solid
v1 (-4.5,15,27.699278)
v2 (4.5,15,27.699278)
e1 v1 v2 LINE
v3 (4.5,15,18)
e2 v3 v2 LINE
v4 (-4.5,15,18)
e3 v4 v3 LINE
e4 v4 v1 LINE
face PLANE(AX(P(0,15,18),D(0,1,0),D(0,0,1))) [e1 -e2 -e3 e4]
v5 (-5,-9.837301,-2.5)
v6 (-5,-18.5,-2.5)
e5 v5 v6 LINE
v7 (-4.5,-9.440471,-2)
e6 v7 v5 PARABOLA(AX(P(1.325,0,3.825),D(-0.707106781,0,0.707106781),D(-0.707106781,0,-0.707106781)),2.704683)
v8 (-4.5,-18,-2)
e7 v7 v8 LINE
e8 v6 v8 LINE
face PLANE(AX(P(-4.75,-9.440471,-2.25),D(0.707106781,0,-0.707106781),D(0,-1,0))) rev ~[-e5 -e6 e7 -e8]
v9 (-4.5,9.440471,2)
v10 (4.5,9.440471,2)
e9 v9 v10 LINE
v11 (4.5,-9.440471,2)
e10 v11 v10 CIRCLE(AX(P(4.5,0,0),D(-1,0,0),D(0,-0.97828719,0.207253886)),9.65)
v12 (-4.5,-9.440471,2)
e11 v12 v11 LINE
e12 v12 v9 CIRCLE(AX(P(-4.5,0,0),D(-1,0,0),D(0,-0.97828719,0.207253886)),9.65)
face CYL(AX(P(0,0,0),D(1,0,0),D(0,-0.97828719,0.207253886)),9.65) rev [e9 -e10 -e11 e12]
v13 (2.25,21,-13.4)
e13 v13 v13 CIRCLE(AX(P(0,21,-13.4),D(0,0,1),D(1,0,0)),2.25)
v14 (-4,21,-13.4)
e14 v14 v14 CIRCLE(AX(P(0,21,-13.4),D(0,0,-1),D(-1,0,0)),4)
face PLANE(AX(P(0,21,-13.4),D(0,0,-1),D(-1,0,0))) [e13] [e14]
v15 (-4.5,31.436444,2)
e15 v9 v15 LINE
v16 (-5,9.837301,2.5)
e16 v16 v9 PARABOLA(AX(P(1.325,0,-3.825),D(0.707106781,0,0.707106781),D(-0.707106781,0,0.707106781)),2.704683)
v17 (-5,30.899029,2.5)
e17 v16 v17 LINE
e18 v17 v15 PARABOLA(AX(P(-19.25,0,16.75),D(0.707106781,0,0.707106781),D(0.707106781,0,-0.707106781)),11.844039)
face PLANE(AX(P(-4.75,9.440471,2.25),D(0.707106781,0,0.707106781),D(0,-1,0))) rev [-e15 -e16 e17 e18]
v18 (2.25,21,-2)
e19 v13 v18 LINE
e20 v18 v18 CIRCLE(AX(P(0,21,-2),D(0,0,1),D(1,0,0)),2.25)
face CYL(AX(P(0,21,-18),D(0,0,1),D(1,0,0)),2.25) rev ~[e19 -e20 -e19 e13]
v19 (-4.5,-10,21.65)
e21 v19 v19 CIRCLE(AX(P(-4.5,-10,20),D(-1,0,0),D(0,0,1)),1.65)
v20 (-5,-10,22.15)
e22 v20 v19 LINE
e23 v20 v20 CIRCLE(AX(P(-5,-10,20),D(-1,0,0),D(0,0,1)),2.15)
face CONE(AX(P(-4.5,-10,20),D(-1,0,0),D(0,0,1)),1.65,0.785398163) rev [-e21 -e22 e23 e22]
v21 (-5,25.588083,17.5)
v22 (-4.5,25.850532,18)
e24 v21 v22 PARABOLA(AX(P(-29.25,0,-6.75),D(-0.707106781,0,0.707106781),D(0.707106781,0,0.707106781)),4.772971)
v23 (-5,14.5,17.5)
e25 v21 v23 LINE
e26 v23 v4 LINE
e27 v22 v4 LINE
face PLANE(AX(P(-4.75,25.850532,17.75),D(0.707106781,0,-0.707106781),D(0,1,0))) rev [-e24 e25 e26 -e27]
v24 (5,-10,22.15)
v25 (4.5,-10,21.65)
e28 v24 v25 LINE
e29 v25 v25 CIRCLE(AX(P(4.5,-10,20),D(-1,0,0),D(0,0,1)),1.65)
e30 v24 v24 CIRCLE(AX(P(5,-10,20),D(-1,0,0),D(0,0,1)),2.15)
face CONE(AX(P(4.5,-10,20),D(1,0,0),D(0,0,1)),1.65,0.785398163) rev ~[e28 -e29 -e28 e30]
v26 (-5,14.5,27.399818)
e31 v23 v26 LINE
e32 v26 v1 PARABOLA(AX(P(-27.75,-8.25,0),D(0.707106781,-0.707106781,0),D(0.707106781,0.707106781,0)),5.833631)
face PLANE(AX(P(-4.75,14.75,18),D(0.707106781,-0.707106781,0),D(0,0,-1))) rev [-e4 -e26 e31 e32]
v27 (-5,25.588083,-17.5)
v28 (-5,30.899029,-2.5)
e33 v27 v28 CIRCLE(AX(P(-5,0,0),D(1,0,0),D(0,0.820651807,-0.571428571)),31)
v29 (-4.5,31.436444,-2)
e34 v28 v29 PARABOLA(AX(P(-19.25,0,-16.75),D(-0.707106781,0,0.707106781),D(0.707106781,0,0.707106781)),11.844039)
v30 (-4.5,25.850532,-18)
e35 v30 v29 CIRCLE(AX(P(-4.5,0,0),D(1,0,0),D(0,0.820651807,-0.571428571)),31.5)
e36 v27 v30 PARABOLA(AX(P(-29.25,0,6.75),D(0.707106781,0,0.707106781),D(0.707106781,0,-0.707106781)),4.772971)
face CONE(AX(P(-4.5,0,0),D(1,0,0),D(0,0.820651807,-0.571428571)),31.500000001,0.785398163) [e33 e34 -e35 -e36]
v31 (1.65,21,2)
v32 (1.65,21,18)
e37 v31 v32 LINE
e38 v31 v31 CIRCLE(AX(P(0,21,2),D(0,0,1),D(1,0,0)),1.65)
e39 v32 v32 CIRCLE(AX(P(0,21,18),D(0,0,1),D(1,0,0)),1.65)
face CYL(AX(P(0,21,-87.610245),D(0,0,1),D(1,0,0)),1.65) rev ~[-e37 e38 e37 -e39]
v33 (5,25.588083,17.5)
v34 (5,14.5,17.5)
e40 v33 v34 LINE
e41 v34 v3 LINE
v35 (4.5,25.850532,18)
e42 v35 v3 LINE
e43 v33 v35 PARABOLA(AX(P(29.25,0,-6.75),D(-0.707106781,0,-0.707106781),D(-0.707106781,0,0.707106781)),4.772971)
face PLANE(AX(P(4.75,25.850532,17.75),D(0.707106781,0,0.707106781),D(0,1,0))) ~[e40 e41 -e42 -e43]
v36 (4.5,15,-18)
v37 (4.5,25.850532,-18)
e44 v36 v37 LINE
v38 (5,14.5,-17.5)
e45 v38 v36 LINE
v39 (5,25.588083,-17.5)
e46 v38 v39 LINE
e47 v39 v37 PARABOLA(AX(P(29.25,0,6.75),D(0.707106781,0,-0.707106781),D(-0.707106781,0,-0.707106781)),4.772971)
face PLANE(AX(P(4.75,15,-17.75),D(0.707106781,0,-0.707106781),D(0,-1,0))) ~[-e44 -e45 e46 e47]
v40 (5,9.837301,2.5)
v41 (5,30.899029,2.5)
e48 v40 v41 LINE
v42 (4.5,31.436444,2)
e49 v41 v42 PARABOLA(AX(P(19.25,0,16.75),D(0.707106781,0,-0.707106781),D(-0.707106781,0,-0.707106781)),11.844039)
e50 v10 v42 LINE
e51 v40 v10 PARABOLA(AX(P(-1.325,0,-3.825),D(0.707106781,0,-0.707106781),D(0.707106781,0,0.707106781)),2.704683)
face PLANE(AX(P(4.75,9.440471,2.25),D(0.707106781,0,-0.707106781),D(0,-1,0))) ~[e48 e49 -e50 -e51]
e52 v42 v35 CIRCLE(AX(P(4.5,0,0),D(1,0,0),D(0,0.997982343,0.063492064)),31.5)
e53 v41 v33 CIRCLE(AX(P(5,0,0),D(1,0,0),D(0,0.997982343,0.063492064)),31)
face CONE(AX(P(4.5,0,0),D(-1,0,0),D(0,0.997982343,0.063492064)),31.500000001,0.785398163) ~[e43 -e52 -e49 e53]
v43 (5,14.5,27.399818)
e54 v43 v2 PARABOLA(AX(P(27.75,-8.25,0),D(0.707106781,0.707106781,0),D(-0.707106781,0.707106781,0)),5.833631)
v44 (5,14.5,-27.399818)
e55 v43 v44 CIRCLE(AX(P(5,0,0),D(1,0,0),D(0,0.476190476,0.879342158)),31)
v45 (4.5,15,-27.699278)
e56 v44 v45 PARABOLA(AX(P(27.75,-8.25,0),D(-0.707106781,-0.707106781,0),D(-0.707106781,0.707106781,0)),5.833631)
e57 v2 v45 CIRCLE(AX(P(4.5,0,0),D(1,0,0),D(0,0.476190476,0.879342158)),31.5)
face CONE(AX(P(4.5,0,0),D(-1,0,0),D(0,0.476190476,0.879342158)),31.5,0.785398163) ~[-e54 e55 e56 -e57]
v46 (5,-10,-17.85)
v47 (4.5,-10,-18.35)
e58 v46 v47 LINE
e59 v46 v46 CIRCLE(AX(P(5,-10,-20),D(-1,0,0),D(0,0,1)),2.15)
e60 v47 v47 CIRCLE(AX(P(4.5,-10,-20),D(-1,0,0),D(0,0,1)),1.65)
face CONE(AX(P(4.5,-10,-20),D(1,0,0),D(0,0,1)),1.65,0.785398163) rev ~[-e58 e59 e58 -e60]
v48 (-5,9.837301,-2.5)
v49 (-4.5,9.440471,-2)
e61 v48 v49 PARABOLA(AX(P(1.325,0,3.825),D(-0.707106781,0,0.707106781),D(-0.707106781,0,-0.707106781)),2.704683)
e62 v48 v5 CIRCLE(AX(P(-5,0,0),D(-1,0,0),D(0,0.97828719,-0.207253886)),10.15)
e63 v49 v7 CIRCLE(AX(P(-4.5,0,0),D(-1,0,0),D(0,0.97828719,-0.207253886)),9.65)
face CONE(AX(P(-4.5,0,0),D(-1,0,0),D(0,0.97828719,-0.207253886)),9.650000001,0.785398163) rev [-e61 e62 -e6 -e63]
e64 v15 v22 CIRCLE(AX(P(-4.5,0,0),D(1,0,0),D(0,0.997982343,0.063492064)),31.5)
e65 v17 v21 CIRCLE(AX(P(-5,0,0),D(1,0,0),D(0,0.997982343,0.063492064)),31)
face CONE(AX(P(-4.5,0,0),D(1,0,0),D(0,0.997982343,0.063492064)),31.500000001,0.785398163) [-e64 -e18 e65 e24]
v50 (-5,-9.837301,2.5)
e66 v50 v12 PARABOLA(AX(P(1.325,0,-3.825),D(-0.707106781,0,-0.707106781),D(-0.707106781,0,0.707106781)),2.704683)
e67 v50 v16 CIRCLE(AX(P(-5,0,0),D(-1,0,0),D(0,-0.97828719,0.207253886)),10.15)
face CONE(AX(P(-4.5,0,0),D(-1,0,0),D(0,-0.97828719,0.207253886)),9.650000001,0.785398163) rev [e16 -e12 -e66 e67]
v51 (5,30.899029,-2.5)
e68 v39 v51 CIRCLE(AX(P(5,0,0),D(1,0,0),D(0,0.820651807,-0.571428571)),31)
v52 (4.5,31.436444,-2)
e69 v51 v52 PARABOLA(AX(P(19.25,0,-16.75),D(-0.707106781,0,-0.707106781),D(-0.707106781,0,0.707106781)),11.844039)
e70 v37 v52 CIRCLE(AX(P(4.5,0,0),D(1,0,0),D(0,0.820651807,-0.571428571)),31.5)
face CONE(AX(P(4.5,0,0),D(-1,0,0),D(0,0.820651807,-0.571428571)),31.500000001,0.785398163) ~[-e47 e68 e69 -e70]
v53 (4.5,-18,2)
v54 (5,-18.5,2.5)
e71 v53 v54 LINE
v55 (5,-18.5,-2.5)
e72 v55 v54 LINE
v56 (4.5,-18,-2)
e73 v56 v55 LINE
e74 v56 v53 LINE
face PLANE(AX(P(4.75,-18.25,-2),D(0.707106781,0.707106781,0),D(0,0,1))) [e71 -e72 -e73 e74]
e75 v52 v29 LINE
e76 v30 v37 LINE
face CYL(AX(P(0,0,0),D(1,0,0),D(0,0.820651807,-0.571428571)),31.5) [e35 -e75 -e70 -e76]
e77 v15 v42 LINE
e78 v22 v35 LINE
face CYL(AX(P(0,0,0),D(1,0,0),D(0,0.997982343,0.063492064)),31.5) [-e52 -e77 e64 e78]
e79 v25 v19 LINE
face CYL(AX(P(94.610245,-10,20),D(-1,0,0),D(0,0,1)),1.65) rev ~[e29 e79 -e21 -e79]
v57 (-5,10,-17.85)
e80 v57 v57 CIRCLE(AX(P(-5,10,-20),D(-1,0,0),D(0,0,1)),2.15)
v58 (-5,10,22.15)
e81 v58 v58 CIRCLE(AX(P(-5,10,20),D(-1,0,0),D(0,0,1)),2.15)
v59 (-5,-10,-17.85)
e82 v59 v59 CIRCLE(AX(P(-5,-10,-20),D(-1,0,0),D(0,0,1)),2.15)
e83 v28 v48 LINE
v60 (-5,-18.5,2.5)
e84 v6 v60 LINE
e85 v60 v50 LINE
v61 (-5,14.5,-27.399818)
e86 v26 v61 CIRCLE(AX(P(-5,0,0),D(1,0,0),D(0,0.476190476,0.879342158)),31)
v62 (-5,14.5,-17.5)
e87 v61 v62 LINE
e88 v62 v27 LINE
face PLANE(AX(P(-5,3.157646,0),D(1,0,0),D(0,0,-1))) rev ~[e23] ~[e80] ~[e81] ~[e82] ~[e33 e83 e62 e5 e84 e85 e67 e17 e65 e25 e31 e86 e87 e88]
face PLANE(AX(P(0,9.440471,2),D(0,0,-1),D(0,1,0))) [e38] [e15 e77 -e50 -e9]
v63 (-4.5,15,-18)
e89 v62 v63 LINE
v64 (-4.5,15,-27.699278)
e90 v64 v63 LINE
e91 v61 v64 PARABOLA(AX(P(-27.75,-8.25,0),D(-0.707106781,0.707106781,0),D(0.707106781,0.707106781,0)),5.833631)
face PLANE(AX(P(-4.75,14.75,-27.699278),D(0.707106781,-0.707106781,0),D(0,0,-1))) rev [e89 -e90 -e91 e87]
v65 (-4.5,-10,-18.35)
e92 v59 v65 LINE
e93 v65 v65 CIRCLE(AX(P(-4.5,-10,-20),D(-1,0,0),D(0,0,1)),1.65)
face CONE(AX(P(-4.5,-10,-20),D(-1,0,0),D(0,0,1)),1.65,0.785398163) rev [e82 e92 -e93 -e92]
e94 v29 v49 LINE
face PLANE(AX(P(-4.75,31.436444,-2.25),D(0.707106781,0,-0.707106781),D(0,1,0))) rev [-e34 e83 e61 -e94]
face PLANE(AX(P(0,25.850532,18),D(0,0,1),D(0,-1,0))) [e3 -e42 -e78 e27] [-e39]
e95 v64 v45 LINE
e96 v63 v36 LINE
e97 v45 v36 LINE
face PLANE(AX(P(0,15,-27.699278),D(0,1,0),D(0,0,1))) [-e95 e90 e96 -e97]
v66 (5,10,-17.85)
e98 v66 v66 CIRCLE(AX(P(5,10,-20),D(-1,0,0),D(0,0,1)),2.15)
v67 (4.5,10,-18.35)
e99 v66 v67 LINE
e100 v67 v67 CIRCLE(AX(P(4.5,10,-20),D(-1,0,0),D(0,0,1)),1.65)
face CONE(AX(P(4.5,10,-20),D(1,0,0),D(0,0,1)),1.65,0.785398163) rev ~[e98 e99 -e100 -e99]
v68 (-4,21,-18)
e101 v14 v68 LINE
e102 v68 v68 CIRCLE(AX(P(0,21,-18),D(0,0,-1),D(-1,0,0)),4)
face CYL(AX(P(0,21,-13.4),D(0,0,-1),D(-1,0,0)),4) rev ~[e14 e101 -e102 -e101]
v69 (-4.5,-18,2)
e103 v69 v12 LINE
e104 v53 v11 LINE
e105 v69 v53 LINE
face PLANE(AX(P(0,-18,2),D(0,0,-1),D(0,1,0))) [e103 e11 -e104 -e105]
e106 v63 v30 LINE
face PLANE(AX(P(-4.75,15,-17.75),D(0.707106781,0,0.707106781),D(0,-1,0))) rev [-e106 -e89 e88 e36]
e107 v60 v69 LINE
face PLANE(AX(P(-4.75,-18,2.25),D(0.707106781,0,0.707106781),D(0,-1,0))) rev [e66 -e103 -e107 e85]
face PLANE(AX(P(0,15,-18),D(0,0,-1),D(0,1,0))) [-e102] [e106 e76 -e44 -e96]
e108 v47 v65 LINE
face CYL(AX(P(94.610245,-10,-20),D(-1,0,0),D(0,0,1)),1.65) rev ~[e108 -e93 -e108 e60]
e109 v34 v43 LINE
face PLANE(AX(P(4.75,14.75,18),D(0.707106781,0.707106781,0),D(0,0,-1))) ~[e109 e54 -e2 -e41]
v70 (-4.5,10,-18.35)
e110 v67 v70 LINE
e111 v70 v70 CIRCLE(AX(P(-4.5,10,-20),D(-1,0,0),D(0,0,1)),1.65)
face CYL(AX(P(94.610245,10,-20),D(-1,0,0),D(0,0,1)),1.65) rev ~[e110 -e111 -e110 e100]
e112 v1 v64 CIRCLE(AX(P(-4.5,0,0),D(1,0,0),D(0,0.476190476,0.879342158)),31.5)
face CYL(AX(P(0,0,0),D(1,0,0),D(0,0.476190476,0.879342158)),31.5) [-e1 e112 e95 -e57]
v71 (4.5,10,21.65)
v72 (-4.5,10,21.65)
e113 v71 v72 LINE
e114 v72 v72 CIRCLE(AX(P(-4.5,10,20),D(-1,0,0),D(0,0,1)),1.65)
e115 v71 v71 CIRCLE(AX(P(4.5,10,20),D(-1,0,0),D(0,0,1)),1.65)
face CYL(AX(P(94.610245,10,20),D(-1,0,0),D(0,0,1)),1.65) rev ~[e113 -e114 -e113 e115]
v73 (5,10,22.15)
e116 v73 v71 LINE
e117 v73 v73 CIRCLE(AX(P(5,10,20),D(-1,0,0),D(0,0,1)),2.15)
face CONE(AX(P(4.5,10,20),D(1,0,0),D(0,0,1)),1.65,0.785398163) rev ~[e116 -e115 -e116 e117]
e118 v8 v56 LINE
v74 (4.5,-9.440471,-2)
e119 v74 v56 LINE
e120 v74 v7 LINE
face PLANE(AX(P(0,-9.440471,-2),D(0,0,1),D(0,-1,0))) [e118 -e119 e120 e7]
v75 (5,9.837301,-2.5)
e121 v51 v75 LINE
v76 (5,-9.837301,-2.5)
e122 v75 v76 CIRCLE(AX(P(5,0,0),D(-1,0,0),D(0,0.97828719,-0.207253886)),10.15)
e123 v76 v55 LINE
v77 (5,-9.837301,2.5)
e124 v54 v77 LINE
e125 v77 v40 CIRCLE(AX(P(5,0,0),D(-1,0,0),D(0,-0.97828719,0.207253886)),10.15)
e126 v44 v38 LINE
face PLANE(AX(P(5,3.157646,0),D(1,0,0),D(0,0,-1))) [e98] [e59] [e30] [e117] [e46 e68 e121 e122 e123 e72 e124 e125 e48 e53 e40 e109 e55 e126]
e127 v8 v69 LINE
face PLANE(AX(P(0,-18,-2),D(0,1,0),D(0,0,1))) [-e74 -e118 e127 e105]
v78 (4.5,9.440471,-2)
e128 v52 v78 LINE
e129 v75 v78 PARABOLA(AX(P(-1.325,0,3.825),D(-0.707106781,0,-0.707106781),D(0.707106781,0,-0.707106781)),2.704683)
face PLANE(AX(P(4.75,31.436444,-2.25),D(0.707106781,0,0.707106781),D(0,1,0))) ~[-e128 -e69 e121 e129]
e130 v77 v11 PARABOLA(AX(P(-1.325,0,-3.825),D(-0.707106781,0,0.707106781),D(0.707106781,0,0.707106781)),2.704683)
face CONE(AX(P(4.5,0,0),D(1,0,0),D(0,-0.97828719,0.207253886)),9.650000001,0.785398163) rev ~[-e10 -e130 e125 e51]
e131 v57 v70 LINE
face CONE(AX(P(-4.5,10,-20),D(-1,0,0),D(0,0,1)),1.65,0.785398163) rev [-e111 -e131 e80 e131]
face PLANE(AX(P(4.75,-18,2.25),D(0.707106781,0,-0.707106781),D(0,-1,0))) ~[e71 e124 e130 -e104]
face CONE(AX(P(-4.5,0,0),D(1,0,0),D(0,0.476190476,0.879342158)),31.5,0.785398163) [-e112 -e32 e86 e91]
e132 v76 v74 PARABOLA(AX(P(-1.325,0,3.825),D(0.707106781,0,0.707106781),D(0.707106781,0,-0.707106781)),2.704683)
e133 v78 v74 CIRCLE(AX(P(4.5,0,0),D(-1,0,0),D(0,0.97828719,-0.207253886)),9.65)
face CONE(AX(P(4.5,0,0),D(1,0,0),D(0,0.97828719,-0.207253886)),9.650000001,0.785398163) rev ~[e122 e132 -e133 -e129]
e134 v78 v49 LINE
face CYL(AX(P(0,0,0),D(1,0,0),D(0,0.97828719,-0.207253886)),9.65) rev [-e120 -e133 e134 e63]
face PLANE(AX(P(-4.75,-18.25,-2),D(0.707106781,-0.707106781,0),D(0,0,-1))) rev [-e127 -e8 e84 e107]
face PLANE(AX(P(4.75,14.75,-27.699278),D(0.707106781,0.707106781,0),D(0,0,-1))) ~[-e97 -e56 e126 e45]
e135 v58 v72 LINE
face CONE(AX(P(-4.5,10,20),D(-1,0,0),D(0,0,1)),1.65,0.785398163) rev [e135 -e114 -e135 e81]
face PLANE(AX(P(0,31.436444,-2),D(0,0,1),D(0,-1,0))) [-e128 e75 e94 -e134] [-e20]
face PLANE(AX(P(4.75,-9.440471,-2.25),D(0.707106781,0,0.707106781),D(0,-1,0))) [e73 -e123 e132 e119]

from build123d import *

# Parameters (mm, degrees)
BOSS_EXTRUDE1_DEPTH                                  = 5
HOLE_SIZE_BY_SOCKET_HEAD_CAP_SCREW_TYPE1_D           = 4.5
HOLE_SIZE_BY_SOCKET_HEAD_CAP_SCREW_TYPE1_DEPTH       = 16
HOLE_SIZE_BY_SOCKET_HEAD_CAP_SCREW_TYPE1_CBORE_D     = 8
HOLE_SIZE_BY_SOCKET_HEAD_CAP_SCREW_TYPE1_CBORE_DEPTH = 4.6
M4_TAPPED_HOLE1_D                                    = 3.3
M4_TAPPED_HOLE2_D                                    = 3.3
CHAMFER1_SIZE                                        = 0.5


with BuildPart() as part:
    # Sketch1 → Boss-Extrude1 (new, symmetric)
    with BuildSketch(Plane(origin=(0, 0, 0), x_dir=(0, 0, -1), z_dir=(1, 0, 0))):
        with BuildLine():
            Line((2, -9.440471387), (2, -18))
            Line((2, -18), (-2, -18))
            Line((-2, -18), (-2, -9.440471387))
            ThreePointArc((-2, -9.440471387), (-9.65, 0), (-2, 9.440471387))
            Line((-2, 9.440471387), (-2, 31.436443819))
            ThreePointArc((-2, 31.436443819), (-10.382706919, 29.739693963), (-18, 25.850531909))
            Line((-18, 25.850531909), (-18, 15))
            Line((-18, 15), (-27.699277969, 15))
            ThreePointArc((-27.699277969, 15), (0, -31.5), (27.699277969, 15))
            Line((27.699277969, 15), (18, 15))
            Line((18, 15), (18, 25.850531909))
            ThreePointArc((18, 25.850531909), (10.382706919, 29.739693963), (2, 31.436443819))
            Line((2, 31.436443819), (2, 9.440471387))
            ThreePointArc((2, 9.440471387), (9.65, 0), (2, -9.440471387))
        make_face()
    extrude(amount=BOSS_EXTRUDE1_DEPTH, both=True)

    # Hole size by socket head cap screw type1
    with Locations(Plane(origin=(0, 0, -18), x_dir=(-1, 0, 0), z_dir=(0, 0, -1))):
        with Locations((0, 21)):
            CounterBoreHole(HOLE_SIZE_BY_SOCKET_HEAD_CAP_SCREW_TYPE1_D / 2, HOLE_SIZE_BY_SOCKET_HEAD_CAP_SCREW_TYPE1_CBORE_D / 2, HOLE_SIZE_BY_SOCKET_HEAD_CAP_SCREW_TYPE1_CBORE_DEPTH, depth=HOLE_SIZE_BY_SOCKET_HEAD_CAP_SCREW_TYPE1_DEPTH)

    # M4 Tapped Hole1 (through all)
    with Locations(Plane(origin=(0, 0, 2), x_dir=(-1, 0, 0), z_dir=(0, 0, -1))):
        with Locations((0, 21)):
            Hole(M4_TAPPED_HOLE1_D / 2)

    # M4 Tapped Hole2 (through all)
    with Locations(Plane(origin=(5, 0, 0), x_dir=(0, 0, -1), z_dir=(1, 0, 0))):
        with Locations((20, 10), (20, -10), (-20, -10), (-20, 10)):
            Hole(M4_TAPPED_HOLE2_D / 2)

    # Chamfer1
    chamfer1_edges = [part.edges().sort_by_distance(p)[0] for p in [
        (5, 0, -9.65),
        (-5, 20.425265955, -18),
        (-5, 15, -22.849638984),
        (5, -13.720235693, -2),
        (-5, -31.5, 0),
        (-5, 15, 22.849638984),
        (-5, 20.425265955, 18),
        (-5, 29.739693963, 10.382706919),
        (-5, 20.438457603, 2),
        (-5, 0, 9.65),
        (-5, -13.720235693, 2),
        (5, -18, 0),
        (-5, -18, 0),
        (-5, -13.720235693, -2),
        (-5, 0, -9.65),
        (-5, 20.438457603, -2),
        (-5, 29.739693963, -10.382706919),
        (5, -13.720235693, 2),
        (5, 0, 9.65),
        (5, 20.438457603, 2),
        (5, 29.739693963, 10.382706919),
        (5, 20.425265955, 18),
        (5, 15, 22.849638984),
        (5, -31.5, 0),
        (5, 29.739693963, -10.382706919),
        (5, 15, -22.849638984),
        (5, 20.425265955, -18),
        (5, 10, 18.35),
        (-5, 10, 18.35),
        (5, -10, 18.35),
        (-5, -10, 18.35),
        (5, -10, -21.65),
        (-5, -10, -21.65),
        (5, 10, -21.65),
        (-5, 10, -21.65),
        (5, 20.438457603, -2),
    ]]
    chamfer(chamfer1_edges, length=CHAMFER1_SIZE)


solid = part.part
